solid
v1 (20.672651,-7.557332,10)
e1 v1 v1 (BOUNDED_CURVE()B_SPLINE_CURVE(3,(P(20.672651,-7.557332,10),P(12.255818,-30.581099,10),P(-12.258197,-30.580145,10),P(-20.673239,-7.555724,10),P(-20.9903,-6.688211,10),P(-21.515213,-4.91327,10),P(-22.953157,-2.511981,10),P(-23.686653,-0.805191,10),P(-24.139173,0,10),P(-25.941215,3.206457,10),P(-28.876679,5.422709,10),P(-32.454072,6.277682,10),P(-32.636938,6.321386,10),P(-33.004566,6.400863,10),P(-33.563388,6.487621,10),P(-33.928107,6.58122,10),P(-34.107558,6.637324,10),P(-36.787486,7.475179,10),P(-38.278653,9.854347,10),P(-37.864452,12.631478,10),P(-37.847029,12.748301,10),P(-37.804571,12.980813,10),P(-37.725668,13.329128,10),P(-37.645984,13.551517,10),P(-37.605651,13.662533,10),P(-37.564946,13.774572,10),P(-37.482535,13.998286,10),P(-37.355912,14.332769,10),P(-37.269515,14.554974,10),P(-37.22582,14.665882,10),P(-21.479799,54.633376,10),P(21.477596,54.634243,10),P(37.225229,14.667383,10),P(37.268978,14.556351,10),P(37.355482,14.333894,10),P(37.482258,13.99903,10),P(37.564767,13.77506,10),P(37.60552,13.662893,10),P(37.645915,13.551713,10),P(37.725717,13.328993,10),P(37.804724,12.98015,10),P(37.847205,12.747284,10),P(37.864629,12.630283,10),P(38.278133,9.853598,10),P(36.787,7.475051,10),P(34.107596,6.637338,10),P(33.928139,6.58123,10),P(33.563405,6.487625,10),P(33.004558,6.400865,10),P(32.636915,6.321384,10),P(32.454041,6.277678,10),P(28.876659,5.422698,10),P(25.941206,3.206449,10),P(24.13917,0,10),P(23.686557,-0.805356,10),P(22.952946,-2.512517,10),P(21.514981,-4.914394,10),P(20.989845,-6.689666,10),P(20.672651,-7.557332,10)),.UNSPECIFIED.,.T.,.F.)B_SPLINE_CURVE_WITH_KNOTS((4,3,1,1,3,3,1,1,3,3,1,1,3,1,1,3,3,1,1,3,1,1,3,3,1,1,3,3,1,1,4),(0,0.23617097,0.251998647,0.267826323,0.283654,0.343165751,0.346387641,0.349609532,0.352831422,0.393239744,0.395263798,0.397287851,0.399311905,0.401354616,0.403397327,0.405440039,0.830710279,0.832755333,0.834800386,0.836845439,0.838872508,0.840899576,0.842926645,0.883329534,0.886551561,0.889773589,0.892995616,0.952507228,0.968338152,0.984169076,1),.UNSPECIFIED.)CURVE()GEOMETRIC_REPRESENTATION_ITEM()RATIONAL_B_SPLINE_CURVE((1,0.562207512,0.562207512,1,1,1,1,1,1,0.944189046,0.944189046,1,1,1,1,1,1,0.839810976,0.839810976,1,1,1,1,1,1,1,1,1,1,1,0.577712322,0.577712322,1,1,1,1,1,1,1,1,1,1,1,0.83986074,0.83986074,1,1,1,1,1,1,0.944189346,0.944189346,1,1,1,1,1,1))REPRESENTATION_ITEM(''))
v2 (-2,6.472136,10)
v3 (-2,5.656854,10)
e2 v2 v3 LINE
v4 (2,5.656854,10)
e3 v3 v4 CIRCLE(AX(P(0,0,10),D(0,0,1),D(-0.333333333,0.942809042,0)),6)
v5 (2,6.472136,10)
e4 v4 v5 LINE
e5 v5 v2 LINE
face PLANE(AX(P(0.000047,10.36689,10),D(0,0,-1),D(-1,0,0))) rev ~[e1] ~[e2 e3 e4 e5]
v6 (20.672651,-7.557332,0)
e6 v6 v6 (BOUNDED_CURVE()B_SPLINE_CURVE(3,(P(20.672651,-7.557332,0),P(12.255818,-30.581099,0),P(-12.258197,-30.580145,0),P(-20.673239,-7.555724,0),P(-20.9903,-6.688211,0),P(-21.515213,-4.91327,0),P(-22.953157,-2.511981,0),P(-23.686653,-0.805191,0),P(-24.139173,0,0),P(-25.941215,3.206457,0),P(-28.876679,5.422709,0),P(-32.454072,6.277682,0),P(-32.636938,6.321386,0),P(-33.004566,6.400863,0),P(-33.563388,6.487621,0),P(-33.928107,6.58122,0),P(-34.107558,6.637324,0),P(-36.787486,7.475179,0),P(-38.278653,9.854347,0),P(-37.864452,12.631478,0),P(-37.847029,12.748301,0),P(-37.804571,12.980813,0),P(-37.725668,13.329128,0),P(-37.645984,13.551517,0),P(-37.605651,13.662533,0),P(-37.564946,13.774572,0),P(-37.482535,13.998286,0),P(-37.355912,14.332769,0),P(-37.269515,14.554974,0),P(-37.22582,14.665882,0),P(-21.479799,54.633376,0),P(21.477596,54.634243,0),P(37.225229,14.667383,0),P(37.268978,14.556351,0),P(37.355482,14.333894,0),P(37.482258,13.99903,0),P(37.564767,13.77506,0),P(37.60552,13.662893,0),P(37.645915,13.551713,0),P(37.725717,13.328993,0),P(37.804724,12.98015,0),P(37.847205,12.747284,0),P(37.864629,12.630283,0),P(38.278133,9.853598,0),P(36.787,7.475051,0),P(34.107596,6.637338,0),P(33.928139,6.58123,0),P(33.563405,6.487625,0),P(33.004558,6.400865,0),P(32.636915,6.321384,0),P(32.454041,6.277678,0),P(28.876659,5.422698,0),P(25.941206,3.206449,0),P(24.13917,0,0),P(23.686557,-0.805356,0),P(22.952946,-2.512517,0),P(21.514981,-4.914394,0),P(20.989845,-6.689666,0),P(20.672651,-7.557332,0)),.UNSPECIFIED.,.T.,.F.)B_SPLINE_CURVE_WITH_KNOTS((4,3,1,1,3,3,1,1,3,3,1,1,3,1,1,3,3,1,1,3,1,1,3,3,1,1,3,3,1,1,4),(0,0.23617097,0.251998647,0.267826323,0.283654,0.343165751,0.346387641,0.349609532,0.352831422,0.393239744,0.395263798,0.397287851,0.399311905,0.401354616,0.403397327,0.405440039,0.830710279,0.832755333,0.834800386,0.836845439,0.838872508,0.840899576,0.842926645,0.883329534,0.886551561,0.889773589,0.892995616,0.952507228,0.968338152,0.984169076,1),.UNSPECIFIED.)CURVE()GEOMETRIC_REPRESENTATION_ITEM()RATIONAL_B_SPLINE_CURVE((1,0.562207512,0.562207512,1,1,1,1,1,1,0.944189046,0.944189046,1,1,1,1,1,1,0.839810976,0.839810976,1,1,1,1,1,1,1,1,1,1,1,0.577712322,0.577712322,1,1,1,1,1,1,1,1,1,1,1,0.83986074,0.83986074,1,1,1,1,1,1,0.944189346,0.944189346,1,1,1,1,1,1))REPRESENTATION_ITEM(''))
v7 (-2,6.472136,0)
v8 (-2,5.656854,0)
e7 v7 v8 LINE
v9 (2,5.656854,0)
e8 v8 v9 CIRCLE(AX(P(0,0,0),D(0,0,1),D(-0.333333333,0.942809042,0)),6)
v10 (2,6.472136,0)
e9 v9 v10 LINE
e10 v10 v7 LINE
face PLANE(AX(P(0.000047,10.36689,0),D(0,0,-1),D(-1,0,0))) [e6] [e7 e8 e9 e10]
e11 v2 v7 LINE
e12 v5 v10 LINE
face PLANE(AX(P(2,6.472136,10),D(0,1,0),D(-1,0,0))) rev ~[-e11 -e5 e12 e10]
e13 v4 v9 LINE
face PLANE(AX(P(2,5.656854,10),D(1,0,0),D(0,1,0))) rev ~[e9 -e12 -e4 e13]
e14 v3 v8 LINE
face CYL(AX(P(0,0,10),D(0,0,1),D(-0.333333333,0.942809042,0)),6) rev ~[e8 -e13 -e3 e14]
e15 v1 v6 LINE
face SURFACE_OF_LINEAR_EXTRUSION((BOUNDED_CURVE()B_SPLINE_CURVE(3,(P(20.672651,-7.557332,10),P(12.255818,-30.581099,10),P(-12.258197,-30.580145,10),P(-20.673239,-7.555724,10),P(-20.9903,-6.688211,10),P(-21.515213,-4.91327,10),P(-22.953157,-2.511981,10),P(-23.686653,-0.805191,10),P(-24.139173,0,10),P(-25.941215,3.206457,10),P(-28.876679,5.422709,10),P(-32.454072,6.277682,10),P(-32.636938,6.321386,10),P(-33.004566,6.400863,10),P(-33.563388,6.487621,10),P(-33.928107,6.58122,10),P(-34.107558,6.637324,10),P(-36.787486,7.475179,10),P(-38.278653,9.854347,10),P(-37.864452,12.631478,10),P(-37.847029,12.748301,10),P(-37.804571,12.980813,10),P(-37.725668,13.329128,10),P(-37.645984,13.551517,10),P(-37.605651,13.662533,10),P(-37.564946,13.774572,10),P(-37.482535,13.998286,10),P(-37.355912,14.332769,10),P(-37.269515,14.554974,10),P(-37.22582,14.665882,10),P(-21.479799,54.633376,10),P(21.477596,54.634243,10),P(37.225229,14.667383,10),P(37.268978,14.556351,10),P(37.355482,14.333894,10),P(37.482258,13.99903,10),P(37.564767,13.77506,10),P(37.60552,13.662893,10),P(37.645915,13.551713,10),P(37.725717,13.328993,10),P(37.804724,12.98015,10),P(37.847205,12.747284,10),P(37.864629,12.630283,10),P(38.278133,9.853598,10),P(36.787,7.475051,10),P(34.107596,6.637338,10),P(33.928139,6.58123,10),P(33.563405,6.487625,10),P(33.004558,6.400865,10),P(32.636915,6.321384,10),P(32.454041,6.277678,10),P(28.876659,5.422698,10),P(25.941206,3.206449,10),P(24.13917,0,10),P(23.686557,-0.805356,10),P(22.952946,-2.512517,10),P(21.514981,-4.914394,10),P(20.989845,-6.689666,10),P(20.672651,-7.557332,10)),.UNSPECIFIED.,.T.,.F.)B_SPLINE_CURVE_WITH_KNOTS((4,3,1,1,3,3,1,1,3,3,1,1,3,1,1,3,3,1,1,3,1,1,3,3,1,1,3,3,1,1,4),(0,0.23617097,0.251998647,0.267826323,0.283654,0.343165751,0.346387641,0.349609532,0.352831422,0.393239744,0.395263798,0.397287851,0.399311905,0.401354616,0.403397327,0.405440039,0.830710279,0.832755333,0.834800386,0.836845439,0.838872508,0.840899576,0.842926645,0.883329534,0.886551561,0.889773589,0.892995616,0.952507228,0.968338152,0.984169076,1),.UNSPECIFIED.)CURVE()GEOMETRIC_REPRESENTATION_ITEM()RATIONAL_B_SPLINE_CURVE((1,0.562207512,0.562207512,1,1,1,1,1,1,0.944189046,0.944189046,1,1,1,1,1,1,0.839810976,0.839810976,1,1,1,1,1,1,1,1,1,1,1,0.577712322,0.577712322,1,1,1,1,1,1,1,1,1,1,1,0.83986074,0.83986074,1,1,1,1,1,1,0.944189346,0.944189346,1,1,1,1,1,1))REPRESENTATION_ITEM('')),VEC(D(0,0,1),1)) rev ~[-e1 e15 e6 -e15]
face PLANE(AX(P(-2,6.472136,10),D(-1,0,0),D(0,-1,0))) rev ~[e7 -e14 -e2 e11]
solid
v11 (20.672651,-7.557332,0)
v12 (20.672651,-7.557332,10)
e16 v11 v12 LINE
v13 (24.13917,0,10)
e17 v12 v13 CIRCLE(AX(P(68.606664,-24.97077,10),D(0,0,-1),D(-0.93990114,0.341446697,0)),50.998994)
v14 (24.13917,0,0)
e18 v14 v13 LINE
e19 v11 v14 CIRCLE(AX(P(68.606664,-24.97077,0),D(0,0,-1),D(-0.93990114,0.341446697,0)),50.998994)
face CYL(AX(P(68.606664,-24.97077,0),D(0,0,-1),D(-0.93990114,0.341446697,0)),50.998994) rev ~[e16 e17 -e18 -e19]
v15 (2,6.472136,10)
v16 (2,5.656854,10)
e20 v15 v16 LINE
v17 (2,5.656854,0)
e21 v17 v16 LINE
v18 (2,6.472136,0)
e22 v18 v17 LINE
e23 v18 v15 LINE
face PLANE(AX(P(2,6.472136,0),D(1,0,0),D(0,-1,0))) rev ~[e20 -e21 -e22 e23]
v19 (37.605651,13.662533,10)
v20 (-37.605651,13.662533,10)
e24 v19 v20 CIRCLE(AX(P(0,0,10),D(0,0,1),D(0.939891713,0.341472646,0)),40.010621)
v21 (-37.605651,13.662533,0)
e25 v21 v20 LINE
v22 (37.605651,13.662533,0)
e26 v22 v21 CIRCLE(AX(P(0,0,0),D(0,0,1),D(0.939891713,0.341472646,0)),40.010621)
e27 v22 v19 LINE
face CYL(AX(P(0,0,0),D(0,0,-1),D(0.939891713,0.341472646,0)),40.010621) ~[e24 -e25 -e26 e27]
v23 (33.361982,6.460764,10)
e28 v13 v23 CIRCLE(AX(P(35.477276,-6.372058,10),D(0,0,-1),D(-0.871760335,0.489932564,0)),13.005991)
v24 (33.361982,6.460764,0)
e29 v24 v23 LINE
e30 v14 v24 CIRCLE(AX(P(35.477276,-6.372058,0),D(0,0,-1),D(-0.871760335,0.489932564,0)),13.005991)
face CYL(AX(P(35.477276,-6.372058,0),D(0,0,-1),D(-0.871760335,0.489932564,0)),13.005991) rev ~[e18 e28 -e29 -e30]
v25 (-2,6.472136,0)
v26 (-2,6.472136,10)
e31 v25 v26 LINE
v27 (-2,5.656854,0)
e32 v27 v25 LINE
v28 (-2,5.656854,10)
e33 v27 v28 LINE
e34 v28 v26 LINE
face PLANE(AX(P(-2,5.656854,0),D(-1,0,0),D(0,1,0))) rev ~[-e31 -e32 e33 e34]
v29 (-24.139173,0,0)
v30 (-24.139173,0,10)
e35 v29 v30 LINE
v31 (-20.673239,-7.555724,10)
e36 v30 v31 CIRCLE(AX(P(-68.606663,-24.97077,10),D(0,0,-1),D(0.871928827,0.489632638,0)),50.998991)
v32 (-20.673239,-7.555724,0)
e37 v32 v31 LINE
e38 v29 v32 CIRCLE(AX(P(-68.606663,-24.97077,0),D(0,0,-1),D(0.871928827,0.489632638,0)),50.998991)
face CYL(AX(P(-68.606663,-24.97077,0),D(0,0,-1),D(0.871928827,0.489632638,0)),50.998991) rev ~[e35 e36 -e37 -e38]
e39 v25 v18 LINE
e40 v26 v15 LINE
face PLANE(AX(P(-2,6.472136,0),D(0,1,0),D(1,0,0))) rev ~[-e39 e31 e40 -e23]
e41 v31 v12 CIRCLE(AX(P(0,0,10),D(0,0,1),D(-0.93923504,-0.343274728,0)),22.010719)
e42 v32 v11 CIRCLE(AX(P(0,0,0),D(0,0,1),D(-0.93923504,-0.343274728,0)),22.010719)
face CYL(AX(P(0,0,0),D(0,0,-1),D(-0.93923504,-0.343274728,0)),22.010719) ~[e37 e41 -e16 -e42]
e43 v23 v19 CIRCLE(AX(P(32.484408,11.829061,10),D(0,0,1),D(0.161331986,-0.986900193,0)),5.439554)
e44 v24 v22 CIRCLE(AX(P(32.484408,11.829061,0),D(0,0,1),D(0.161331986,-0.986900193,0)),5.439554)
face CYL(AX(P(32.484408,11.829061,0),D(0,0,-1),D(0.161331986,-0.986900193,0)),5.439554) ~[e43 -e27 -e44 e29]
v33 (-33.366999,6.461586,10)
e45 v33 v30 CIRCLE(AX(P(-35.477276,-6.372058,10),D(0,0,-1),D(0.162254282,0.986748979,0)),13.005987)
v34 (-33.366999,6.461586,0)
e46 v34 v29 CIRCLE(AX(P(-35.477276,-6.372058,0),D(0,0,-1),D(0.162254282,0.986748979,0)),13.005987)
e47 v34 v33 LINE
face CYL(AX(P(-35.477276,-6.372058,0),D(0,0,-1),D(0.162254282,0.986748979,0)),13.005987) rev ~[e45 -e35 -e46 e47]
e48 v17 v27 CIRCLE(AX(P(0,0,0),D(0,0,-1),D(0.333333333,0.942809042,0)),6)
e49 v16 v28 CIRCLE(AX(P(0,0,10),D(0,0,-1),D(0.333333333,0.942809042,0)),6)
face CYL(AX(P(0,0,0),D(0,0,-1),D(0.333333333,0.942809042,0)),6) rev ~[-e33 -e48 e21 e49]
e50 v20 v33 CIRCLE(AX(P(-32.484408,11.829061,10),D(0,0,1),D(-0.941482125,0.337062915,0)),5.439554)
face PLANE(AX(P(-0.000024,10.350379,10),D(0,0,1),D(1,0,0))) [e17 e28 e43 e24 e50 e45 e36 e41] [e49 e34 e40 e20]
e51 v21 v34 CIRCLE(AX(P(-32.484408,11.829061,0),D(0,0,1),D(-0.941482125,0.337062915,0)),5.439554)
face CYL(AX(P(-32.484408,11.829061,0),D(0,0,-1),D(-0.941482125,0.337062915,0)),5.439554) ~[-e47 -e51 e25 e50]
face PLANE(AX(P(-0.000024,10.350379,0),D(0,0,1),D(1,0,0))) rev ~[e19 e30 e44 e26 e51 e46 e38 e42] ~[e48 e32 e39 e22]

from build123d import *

# Parameters (mm, degrees)
EXTRUDE_1_DEPTH = 10
EXTRUDE_2_DEPTH = 10


with BuildPart() as part:
    # 草图1 → 凸台-拉伸1 (new body)
    with BuildSketch(Plane.XY):
        with BuildLine():
            ThreePointArc((-20.67323893, -7.555723727), (-0.000856312, -22.010719392), (20.672650967, -7.557332261))
            ThreePointArc((20.672650967, -7.557332261), (22.251643113, -3.707904383), (24.139169609, 0))
            ThreePointArc((24.139169609, 0), (28.015114123, 4.280261917), (33.361982334, 6.460763761))
            ThreePointArc((33.361982334, 6.460763761), (37.170858971, 9.06755238), (37.605651194, 13.66253267))
            ThreePointArc((37.605651194, 13.66253267), (0, 40.010621099), (-37.605651194, 13.66253267))
            ThreePointArc((-37.605651194, 13.66253267), (-37.172148925, 9.069742682), (-33.366999211, 6.461586294))
            ThreePointArc((-33.366999211, 6.461586294), (-28.017198894, 4.281717924), (-24.139173474, 0))
            ThreePointArc((-24.139173474, 0), (-22.252003596, -3.707126596), (-20.67323893, -7.555723727))
        make_face()
        with BuildLine():
            Line((-2, 6.47213596), (2, 6.47213596))
            Line((2, 6.47213596), (2, 5.656854249))
            ThreePointArc((2, 5.656854249), (0, -6), (-2, 5.656854249))
            Line((-2, 5.656854249), (-2, 6.47213596))
        make_face(mode=Mode.SUBTRACT)
    extrude(amount=EXTRUDE_1_DEPTH)


with BuildPart() as body_2:
    # 草图3 → 凸台-拉伸2 (new body)
    with BuildSketch(Plane.XY.offset(10)):
        with BuildLine():
            add(Edge.make_bspline(
                [(20.672650967, -7.557332261), (12.255817701, -30.58109916), (-12.258197138, -30.580145458), (-20.67323893, -7.555723727), (-20.990300477, -6.688210655), (-21.515212971, -4.91326986), (-22.953157447, -2.511981493), (-23.686653077, -0.805190812), (-24.139173474, 0), (-25.941214888, 3.206456984), (-28.876678607, 5.422708865), (-32.454071535, 6.277682245), (-32.636937817, 6.321386084), (-33.004565746, 6.400863146), (-33.563388497, 6.487620787), (-33.928107149, 6.581220009), (-34.107557676, 6.637323584), (-36.787486418, 7.475178936), (-38.278653204, 9.854347125), (-37.864452375, 12.631478258), (-37.847028543, 12.748301458), (-37.804570723, 12.980812826), (-37.72566755, 13.329128382), (-37.645984376, 13.551516975), (-37.605651194, 13.66253267), (-37.564946219, 13.774571714), (-37.48253487, 13.998285985), (-37.355911981, 14.332769126), (-37.26951473, 14.554974482), (-37.225820462, 14.665881892), (-21.479799392, 54.633376357), (21.477595695, 54.634242717), (37.225228872, 14.667383412), (37.268977717, 14.556350604), (37.355481864, 14.333893514), (37.482258323, 13.999029952), (37.56476746, 13.775060386), (37.605520182, 13.662893272), (37.645914509, 13.551712597), (37.725717048, 13.32899297), (37.804724121, 12.980149933), (37.847204837, 12.747284474), (37.864628645, 12.630283384), (38.278132711, 9.853598325), (36.7869997, 7.475050895), (34.107596424, 6.637337571), (33.928138685, 6.58123025), (33.563404971, 6.487625083), (33.004557992, 6.400865062), (32.636914529, 6.321384074), (32.45404057, 6.277677938), (28.876659191, 5.42269827), (25.941206083, 3.206448551), (24.139169924, -1.77e-07), (23.686556798, -0.805356259), (22.952946086, -2.512516997), (21.514980993, -4.914393573), (20.989845079, -6.689665876), (20.672650967, -7.557332261)],
                knots=[0, 0, 0, 0, 0.23617097, 0.23617097, 0.23617097, 0.251998647, 0.267826323, 0.283654, 0.283654, 0.283654, 0.343165751, 0.343165751, 0.343165751, 0.346387641, 0.349609532, 0.352831422, 0.352831422, 0.352831422, 0.393239744, 0.393239744, 0.393239744, 0.395263798, 0.397287851, 0.399311905, 0.399311905, 0.399311905, 0.401354616, 0.403397327, 0.405440039, 0.405440039, 0.405440039, 0.830710279, 0.830710279, 0.830710279, 0.832755333, 0.834800386, 0.836845439, 0.836845439, 0.836845439, 0.838872508, 0.840899576, 0.842926645, 0.842926645, 0.842926645, 0.883329534, 0.883329534, 0.883329534, 0.886551561, 0.889773589, 0.892995616, 0.892995616, 0.892995616, 0.952507228, 0.952507228, 0.952507228, 0.968338152, 0.984169076, 1, 1, 1, 1], degree=3, weights=[1, 0.562207512, 0.562207512, 1, 1, 1, 1, 1, 1, 0.944189046, 0.944189046, 1, 1, 1, 1, 1, 1, 0.839810976, 0.839810976, 1, 1, 1, 1, 1, 1, 1, 1, 1, 1, 1, 0.577712322, 0.577712322, 1, 1, 1, 1, 1, 1, 1, 1, 1, 1, 1, 0.83986074, 0.83986074, 1, 1, 1, 1, 1, 1, 0.944189346, 0.944189346, 1, 1, 1, 1, 1, 1]))
        make_face()
        with BuildLine():
            Line((-2, 6.47213596), (-2, 5.656854249))
            ThreePointArc((-2, 5.656854249), (0, -6), (2, 5.656854249))
            Line((2, 5.656854249), (2, 6.47213596))
            Line((2, 6.47213596), (-2, 6.47213596))
        make_face(mode=Mode.SUBTRACT)
    extrude(amount=-EXTRUDE_2_DEPTH)


solid = Compound([part.part, body_2.part])
